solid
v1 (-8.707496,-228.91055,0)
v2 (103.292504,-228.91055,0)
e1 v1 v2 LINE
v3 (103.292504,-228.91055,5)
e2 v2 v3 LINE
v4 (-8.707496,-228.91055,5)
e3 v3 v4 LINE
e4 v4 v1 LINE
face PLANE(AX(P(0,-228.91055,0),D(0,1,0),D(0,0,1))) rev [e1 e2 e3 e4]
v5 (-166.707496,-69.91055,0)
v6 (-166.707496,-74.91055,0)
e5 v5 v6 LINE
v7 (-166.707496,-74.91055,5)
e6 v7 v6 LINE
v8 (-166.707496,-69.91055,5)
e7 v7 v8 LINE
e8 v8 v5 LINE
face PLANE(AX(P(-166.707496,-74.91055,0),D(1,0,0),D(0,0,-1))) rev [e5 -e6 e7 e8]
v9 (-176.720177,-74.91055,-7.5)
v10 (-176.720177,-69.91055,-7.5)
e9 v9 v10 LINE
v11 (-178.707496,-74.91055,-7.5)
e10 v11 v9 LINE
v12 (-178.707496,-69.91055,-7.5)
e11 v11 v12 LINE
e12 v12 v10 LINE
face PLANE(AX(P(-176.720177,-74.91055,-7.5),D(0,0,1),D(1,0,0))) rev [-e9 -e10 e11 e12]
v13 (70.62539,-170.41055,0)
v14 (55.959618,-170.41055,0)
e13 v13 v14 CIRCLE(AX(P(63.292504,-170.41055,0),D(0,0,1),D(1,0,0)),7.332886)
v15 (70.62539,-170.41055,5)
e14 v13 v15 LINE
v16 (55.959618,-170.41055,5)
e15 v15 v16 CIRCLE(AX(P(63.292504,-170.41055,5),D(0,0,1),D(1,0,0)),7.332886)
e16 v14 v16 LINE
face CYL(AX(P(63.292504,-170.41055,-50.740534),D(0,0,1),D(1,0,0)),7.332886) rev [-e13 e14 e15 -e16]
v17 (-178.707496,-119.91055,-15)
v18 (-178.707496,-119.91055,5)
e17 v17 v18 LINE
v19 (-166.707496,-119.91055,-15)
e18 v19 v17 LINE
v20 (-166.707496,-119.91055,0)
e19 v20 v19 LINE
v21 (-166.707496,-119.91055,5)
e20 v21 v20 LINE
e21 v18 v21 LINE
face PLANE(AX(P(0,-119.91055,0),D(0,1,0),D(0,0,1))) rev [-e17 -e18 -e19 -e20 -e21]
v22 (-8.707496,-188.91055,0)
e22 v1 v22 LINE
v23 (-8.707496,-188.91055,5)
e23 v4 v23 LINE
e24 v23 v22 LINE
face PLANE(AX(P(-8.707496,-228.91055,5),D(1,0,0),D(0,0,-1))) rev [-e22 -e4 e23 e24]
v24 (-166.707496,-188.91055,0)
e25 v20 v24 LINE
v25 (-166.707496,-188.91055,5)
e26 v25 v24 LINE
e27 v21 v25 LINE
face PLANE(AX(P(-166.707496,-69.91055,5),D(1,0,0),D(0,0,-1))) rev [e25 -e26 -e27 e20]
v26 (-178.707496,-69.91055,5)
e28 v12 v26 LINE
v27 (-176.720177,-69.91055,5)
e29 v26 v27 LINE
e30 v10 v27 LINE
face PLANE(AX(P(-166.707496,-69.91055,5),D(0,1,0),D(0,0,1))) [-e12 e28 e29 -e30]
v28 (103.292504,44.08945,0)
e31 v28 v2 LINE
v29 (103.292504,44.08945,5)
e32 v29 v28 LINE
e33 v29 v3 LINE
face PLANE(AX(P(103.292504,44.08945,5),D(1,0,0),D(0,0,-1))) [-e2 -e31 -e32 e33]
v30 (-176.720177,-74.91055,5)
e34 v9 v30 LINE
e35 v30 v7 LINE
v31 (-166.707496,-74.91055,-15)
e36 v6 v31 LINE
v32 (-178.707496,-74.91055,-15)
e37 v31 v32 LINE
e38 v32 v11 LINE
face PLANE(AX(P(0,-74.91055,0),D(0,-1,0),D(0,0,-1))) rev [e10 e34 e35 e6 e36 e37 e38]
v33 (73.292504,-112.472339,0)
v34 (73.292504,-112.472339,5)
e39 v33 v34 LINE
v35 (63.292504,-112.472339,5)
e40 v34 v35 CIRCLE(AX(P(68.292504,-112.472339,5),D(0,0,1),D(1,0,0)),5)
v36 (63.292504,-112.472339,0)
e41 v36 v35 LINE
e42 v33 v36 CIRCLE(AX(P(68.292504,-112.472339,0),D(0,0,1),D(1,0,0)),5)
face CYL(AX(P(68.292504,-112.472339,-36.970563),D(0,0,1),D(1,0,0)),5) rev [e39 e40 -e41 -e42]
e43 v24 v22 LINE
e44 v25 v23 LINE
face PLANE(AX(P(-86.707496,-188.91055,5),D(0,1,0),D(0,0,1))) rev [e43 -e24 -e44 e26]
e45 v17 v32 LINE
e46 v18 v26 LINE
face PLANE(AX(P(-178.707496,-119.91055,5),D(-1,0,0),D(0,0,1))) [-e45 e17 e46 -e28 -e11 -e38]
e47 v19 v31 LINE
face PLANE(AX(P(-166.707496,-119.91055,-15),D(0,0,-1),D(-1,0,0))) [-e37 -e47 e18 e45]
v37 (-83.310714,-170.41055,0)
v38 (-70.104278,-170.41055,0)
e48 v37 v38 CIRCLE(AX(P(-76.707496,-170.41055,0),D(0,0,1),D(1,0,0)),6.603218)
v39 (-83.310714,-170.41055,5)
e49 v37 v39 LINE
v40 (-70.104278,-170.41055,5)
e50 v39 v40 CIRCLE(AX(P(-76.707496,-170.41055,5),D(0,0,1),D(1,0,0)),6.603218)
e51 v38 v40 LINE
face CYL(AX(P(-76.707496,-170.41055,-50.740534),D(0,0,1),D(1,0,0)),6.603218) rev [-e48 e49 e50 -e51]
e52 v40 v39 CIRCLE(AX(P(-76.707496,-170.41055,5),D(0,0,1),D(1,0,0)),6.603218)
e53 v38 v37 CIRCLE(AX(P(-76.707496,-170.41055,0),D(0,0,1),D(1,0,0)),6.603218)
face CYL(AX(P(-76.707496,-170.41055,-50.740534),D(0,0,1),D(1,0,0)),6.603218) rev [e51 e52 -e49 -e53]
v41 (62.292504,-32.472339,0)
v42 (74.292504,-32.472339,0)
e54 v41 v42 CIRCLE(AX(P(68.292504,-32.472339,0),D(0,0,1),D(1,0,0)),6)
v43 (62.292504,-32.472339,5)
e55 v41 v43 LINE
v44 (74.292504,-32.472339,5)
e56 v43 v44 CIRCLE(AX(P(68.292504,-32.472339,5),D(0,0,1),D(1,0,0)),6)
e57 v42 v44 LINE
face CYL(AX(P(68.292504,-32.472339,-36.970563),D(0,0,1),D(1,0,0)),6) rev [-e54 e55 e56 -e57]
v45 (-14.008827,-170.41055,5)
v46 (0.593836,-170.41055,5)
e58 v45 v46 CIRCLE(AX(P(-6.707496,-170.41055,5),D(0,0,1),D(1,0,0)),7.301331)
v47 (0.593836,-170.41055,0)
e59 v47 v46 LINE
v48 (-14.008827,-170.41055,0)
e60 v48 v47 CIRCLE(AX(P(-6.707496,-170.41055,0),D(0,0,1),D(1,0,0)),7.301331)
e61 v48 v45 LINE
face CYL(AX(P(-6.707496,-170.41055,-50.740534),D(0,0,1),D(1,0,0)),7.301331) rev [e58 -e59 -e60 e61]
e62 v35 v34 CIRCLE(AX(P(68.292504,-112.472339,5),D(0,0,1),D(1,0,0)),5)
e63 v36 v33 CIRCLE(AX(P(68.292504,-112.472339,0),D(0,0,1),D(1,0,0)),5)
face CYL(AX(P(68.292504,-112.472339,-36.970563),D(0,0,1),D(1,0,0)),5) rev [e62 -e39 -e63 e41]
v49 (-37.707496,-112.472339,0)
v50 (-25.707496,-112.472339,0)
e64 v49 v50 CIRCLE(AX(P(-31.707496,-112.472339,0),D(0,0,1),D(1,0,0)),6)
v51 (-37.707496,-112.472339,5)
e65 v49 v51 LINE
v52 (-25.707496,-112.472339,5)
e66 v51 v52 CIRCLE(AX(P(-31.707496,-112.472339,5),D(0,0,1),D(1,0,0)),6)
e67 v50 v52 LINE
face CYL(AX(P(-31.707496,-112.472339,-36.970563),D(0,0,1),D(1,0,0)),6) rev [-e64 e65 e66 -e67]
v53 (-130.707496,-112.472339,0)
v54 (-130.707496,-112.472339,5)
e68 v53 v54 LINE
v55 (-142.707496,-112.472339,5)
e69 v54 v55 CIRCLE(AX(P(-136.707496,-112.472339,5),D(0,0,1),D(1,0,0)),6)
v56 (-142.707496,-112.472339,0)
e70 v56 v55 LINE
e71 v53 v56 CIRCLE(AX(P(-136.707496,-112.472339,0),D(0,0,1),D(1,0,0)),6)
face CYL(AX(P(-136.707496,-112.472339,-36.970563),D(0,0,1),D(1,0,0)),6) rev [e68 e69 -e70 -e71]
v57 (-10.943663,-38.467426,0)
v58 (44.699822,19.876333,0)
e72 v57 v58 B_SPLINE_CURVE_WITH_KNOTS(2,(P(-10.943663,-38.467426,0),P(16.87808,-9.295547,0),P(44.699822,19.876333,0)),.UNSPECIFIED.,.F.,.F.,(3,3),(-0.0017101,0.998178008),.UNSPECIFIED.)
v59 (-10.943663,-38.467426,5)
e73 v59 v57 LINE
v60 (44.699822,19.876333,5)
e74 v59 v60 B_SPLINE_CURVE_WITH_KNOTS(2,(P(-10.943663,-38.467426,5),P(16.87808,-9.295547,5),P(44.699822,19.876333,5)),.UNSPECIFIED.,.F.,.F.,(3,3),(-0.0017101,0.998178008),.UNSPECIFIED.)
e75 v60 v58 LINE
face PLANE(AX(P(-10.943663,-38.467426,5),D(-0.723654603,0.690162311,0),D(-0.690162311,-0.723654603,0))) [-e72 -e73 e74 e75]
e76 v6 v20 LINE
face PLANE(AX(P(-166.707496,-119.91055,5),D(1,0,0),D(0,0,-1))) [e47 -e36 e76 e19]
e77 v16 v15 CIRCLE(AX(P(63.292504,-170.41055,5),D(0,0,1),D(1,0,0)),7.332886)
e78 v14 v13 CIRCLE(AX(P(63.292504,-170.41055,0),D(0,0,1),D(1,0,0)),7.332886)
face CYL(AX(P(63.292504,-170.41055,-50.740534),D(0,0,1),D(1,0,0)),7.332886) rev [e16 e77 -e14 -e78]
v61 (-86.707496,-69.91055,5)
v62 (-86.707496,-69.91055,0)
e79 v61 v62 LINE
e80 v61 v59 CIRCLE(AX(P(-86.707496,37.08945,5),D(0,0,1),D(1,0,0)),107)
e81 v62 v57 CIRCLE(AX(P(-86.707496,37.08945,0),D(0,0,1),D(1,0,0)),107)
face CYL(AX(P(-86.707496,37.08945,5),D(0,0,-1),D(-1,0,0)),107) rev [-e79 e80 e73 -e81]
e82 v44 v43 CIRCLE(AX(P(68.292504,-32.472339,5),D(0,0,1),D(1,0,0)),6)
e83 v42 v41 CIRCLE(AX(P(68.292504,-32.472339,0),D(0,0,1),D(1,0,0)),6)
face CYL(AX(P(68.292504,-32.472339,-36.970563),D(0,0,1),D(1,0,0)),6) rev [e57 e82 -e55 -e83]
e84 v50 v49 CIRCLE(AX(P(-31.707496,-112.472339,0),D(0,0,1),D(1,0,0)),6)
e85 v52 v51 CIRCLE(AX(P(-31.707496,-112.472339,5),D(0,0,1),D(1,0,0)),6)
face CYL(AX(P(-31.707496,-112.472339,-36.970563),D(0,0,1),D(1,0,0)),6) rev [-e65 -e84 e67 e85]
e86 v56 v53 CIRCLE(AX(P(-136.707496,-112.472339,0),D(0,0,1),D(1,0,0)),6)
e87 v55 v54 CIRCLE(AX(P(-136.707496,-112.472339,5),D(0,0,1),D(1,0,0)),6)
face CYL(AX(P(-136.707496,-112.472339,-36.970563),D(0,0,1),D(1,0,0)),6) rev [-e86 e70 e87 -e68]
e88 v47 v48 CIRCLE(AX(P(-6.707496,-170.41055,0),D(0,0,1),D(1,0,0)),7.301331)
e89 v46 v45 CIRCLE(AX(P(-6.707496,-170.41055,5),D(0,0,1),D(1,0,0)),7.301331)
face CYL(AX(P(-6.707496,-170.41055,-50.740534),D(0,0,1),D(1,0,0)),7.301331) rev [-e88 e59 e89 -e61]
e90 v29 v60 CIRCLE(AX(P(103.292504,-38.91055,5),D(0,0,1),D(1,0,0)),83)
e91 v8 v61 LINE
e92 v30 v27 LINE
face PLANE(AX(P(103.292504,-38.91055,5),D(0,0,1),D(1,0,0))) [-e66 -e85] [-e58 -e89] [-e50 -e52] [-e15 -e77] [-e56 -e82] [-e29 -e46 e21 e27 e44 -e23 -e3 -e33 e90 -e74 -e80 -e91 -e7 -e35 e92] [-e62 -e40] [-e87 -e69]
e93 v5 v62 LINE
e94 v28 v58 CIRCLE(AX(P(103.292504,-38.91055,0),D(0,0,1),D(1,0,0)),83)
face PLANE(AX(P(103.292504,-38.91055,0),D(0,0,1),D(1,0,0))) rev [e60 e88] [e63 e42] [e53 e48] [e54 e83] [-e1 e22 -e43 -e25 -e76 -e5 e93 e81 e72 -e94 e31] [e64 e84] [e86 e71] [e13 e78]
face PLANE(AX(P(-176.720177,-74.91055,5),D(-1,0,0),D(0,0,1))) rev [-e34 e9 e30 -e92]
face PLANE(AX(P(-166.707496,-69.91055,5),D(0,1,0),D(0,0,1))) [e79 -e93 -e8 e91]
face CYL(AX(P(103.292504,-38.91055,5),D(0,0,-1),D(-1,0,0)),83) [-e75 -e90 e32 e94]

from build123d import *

# Parameters (mm, degrees)
EXTRUDE_3_DEPTH     = 5
SKETCH_2_W          = 12
SKETCH_2_H          = 20
EXTRUDE_4_DEPTH     = 50
CUT_EXTRUDE_1_DEPTH = 5
SKETCH_4_W          = 112
SKETCH_4_H          = 5
EXTRUDE_5_DEPTH     = 40
CUT_EXTRUDE_2_REACH = 1236.326
SKETCH_5_R          = 6
SKETCH_5_R_2        = 5
CUT_EXTRUDE_3_REACH = 1236.529
SKETCH_6_R          = 7.332886018
SKETCH_6_R_2        = 7.301331484
SKETCH_6_R_3        = 6.603217824


with BuildPart() as part:
    # 草图1 → 凸台-拉伸3 (new body)
    with BuildSketch(Plane.XY):
        with BuildLine():
            Line((-86.707495778, -188.910549606), (103.292504222, -188.910549606))
            Line((103.292504222, -188.910549606), (103.292504222, 44.089450394))
            ThreePointArc((103.292504222, 44.089450394), (71.593223998, 37.797700493), (44.699821924, 19.876333124))
            add(Edge.make_bspline(
                [(-10.94366291, -38.46742639), (16.878079507, -9.295546633), (44.699821924, 19.876333124)],
                knots=[-0.0017101, -0.0017101, -0.0017101, 0.998178008, 0.998178008, 0.998178008], degree=2))
            ThreePointArc((-10.94366291, -38.46742639), (-45.692777784, -61.737635508), (-86.707495778, -69.910549606))
            Line((-86.707495778, -69.910549606), (-166.707495778, -69.910549606))
            Line((-166.707495778, -69.910549606), (-166.707495778, -188.910549606))
            Line((-166.707495778, -188.910549606), (-86.707495778, -188.910549606))
        make_face()
    extrude(amount=EXTRUDE_3_DEPTH)

    # 草图2 → 凸台-拉伸4 (add)
    with BuildSketch(Plane(origin=(0, -69.910549606, 0), x_dir=(1, 0, 0), z_dir=(0, 1, 0))):
        with Locations((-172.707495778, 5)):
            Rectangle(SKETCH_2_W, SKETCH_2_H)
    extrude(amount=-EXTRUDE_4_DEPTH)

    # 草图3 → 切除-拉伸1 (cut)
    with BuildSketch(Plane(origin=(0, -69.910549606, 0), x_dir=(1, 0, 0), z_dir=(0, 1, 0))):
        Polygon((-166.707495778, 0), (-166.707495778, -5), (-176.720177385, -5), (-176.720177385, 7.5), (-178.707495778, 7.5), (-178.707495778, 15), (-166.707495778, 15), align=None)
    extrude(amount=-CUT_EXTRUDE_1_DEPTH, mode=Mode.SUBTRACT)

    # 草图4 → 凸台-拉伸5 (add)
    with BuildSketch(Plane.XZ.offset(188.910549606)):
        with Locations((47.292504222, 2.5)):
            Rectangle(SKETCH_4_W, SKETCH_4_H)
    extrude(amount=EXTRUDE_5_DEPTH)

    # 草图5 → 切除-拉伸2 (cut, up to next)
    with BuildSketch(Plane(origin=(703.41878585, 634.231928171, 5), x_dir=(0, 1, 0), z_dir=(0, 0, 1)), mode=Mode.PRIVATE) as cut_extrude_2_sk1:
        with Locations(Location((-666.704267343, 635.126281628, 0), (0, 0, 270))):
            Circle(SKETCH_5_R)
    cut_extrude_2_tool1 = extrude(cut_extrude_2_sk1.sketch, amount=-CUT_EXTRUDE_2_REACH, mode=Mode.PRIVATE) & part.part
    # 草图5 → 切除-拉伸2 (cut, up to next)
    with BuildSketch(Plane(origin=(703.41878585, 634.231928171, 5), x_dir=(0, 1, 0), z_dir=(0, 0, 1)), mode=Mode.PRIVATE) as cut_extrude_2_sk2:
        with Locations(Location((-746.704267343, 635.126281628, 0), (0, 0, 270))):
            Circle(SKETCH_5_R_2)
    cut_extrude_2_tool2 = extrude(cut_extrude_2_sk2.sketch, amount=-CUT_EXTRUDE_2_REACH, mode=Mode.PRIVATE) & part.part
    # 草图5 → 切除-拉伸2 (cut, up to next)
    with BuildSketch(Plane(origin=(703.41878585, 634.231928171, 5), x_dir=(0, 1, 0), z_dir=(0, 0, 1)), mode=Mode.PRIVATE) as cut_extrude_2_sk3:
        with Locations(Location((-746.704267343, 840.126281628, 0), (0, 0, 270))):
            Circle(SKETCH_5_R)
    cut_extrude_2_tool3 = extrude(cut_extrude_2_sk3.sketch, amount=-CUT_EXTRUDE_2_REACH, mode=Mode.PRIVATE) & part.part
    # 草图5 → 切除-拉伸2 (cut, up to next)
    with BuildSketch(Plane(origin=(703.41878585, 634.231928171, 5), x_dir=(0, 1, 0), z_dir=(0, 0, 1)), mode=Mode.PRIVATE) as cut_extrude_2_sk4:
        with Locations(Location((-746.704267343, 735.126281628, 0), (0, 0, 270))):
            Circle(SKETCH_5_R)
    cut_extrude_2_tool4 = extrude(cut_extrude_2_sk4.sketch, amount=-CUT_EXTRUDE_2_REACH, mode=Mode.PRIVATE) & part.part
    add(cut_extrude_2_tool1.solids().sort_by_distance((68.292504, -32.472339, 5))[0], mode=Mode.SUBTRACT)
    add(cut_extrude_2_tool2.solids().sort_by_distance((68.292504, -112.472339, 5))[0], mode=Mode.SUBTRACT)
    add(cut_extrude_2_tool3.solids().sort_by_distance((-136.707496, -112.472339, 5))[0], mode=Mode.SUBTRACT)
    add(cut_extrude_2_tool4.solids().sort_by_distance((-31.707496, -112.472339, 5))[0], mode=Mode.SUBTRACT)

    # 草图6 → 切除-拉伸3 (cut, up to next)
    with BuildSketch(Plane(origin=(703.41878585, 634.231928171, 15), x_dir=(0, 1, 0), z_dir=(0, 0, 1)), mode=Mode.PRIVATE) as cut_extrude_3_sk1:
        with Locations(Location((-804.642477777, 640.126281628, 0), (0, 0, 270))):
            Circle(SKETCH_6_R)
    cut_extrude_3_tool1 = extrude(cut_extrude_3_sk1.sketch, amount=-CUT_EXTRUDE_3_REACH, mode=Mode.PRIVATE) & part.part
    # 草图6 → 切除-拉伸3 (cut, up to next)
    with BuildSketch(Plane(origin=(703.41878585, 634.231928171, 15), x_dir=(0, 1, 0), z_dir=(0, 0, 1)), mode=Mode.PRIVATE) as cut_extrude_3_sk2:
        with Locations(Location((-804.642477777, 710.126281628, 0), (0, 0, 270))):
            Circle(SKETCH_6_R_2)
    cut_extrude_3_tool2 = extrude(cut_extrude_3_sk2.sketch, amount=-CUT_EXTRUDE_3_REACH, mode=Mode.PRIVATE) & part.part
    # 草图6 → 切除-拉伸3 (cut, up to next)
    with BuildSketch(Plane(origin=(703.41878585, 634.231928171, 15), x_dir=(0, 1, 0), z_dir=(0, 0, 1)), mode=Mode.PRIVATE) as cut_extrude_3_sk3:
        with Locations(Location((-804.642477777, 780.126281628, 0), (0, 0, 270))):
            Circle(SKETCH_6_R_3)
    cut_extrude_3_tool3 = extrude(cut_extrude_3_sk3.sketch, amount=-CUT_EXTRUDE_3_REACH, mode=Mode.PRIVATE) & part.part
    add(cut_extrude_3_tool1.solids().sort_by_distance((63.292504, -170.41055, 15))[0], mode=Mode.SUBTRACT)
    add(cut_extrude_3_tool2.solids().sort_by_distance((-6.707496, -170.41055, 15))[0], mode=Mode.SUBTRACT)
    add(cut_extrude_3_tool3.solids().sort_by_distance((-76.707496, -170.41055, 15))[0], mode=Mode.SUBTRACT)


solid = part.part
